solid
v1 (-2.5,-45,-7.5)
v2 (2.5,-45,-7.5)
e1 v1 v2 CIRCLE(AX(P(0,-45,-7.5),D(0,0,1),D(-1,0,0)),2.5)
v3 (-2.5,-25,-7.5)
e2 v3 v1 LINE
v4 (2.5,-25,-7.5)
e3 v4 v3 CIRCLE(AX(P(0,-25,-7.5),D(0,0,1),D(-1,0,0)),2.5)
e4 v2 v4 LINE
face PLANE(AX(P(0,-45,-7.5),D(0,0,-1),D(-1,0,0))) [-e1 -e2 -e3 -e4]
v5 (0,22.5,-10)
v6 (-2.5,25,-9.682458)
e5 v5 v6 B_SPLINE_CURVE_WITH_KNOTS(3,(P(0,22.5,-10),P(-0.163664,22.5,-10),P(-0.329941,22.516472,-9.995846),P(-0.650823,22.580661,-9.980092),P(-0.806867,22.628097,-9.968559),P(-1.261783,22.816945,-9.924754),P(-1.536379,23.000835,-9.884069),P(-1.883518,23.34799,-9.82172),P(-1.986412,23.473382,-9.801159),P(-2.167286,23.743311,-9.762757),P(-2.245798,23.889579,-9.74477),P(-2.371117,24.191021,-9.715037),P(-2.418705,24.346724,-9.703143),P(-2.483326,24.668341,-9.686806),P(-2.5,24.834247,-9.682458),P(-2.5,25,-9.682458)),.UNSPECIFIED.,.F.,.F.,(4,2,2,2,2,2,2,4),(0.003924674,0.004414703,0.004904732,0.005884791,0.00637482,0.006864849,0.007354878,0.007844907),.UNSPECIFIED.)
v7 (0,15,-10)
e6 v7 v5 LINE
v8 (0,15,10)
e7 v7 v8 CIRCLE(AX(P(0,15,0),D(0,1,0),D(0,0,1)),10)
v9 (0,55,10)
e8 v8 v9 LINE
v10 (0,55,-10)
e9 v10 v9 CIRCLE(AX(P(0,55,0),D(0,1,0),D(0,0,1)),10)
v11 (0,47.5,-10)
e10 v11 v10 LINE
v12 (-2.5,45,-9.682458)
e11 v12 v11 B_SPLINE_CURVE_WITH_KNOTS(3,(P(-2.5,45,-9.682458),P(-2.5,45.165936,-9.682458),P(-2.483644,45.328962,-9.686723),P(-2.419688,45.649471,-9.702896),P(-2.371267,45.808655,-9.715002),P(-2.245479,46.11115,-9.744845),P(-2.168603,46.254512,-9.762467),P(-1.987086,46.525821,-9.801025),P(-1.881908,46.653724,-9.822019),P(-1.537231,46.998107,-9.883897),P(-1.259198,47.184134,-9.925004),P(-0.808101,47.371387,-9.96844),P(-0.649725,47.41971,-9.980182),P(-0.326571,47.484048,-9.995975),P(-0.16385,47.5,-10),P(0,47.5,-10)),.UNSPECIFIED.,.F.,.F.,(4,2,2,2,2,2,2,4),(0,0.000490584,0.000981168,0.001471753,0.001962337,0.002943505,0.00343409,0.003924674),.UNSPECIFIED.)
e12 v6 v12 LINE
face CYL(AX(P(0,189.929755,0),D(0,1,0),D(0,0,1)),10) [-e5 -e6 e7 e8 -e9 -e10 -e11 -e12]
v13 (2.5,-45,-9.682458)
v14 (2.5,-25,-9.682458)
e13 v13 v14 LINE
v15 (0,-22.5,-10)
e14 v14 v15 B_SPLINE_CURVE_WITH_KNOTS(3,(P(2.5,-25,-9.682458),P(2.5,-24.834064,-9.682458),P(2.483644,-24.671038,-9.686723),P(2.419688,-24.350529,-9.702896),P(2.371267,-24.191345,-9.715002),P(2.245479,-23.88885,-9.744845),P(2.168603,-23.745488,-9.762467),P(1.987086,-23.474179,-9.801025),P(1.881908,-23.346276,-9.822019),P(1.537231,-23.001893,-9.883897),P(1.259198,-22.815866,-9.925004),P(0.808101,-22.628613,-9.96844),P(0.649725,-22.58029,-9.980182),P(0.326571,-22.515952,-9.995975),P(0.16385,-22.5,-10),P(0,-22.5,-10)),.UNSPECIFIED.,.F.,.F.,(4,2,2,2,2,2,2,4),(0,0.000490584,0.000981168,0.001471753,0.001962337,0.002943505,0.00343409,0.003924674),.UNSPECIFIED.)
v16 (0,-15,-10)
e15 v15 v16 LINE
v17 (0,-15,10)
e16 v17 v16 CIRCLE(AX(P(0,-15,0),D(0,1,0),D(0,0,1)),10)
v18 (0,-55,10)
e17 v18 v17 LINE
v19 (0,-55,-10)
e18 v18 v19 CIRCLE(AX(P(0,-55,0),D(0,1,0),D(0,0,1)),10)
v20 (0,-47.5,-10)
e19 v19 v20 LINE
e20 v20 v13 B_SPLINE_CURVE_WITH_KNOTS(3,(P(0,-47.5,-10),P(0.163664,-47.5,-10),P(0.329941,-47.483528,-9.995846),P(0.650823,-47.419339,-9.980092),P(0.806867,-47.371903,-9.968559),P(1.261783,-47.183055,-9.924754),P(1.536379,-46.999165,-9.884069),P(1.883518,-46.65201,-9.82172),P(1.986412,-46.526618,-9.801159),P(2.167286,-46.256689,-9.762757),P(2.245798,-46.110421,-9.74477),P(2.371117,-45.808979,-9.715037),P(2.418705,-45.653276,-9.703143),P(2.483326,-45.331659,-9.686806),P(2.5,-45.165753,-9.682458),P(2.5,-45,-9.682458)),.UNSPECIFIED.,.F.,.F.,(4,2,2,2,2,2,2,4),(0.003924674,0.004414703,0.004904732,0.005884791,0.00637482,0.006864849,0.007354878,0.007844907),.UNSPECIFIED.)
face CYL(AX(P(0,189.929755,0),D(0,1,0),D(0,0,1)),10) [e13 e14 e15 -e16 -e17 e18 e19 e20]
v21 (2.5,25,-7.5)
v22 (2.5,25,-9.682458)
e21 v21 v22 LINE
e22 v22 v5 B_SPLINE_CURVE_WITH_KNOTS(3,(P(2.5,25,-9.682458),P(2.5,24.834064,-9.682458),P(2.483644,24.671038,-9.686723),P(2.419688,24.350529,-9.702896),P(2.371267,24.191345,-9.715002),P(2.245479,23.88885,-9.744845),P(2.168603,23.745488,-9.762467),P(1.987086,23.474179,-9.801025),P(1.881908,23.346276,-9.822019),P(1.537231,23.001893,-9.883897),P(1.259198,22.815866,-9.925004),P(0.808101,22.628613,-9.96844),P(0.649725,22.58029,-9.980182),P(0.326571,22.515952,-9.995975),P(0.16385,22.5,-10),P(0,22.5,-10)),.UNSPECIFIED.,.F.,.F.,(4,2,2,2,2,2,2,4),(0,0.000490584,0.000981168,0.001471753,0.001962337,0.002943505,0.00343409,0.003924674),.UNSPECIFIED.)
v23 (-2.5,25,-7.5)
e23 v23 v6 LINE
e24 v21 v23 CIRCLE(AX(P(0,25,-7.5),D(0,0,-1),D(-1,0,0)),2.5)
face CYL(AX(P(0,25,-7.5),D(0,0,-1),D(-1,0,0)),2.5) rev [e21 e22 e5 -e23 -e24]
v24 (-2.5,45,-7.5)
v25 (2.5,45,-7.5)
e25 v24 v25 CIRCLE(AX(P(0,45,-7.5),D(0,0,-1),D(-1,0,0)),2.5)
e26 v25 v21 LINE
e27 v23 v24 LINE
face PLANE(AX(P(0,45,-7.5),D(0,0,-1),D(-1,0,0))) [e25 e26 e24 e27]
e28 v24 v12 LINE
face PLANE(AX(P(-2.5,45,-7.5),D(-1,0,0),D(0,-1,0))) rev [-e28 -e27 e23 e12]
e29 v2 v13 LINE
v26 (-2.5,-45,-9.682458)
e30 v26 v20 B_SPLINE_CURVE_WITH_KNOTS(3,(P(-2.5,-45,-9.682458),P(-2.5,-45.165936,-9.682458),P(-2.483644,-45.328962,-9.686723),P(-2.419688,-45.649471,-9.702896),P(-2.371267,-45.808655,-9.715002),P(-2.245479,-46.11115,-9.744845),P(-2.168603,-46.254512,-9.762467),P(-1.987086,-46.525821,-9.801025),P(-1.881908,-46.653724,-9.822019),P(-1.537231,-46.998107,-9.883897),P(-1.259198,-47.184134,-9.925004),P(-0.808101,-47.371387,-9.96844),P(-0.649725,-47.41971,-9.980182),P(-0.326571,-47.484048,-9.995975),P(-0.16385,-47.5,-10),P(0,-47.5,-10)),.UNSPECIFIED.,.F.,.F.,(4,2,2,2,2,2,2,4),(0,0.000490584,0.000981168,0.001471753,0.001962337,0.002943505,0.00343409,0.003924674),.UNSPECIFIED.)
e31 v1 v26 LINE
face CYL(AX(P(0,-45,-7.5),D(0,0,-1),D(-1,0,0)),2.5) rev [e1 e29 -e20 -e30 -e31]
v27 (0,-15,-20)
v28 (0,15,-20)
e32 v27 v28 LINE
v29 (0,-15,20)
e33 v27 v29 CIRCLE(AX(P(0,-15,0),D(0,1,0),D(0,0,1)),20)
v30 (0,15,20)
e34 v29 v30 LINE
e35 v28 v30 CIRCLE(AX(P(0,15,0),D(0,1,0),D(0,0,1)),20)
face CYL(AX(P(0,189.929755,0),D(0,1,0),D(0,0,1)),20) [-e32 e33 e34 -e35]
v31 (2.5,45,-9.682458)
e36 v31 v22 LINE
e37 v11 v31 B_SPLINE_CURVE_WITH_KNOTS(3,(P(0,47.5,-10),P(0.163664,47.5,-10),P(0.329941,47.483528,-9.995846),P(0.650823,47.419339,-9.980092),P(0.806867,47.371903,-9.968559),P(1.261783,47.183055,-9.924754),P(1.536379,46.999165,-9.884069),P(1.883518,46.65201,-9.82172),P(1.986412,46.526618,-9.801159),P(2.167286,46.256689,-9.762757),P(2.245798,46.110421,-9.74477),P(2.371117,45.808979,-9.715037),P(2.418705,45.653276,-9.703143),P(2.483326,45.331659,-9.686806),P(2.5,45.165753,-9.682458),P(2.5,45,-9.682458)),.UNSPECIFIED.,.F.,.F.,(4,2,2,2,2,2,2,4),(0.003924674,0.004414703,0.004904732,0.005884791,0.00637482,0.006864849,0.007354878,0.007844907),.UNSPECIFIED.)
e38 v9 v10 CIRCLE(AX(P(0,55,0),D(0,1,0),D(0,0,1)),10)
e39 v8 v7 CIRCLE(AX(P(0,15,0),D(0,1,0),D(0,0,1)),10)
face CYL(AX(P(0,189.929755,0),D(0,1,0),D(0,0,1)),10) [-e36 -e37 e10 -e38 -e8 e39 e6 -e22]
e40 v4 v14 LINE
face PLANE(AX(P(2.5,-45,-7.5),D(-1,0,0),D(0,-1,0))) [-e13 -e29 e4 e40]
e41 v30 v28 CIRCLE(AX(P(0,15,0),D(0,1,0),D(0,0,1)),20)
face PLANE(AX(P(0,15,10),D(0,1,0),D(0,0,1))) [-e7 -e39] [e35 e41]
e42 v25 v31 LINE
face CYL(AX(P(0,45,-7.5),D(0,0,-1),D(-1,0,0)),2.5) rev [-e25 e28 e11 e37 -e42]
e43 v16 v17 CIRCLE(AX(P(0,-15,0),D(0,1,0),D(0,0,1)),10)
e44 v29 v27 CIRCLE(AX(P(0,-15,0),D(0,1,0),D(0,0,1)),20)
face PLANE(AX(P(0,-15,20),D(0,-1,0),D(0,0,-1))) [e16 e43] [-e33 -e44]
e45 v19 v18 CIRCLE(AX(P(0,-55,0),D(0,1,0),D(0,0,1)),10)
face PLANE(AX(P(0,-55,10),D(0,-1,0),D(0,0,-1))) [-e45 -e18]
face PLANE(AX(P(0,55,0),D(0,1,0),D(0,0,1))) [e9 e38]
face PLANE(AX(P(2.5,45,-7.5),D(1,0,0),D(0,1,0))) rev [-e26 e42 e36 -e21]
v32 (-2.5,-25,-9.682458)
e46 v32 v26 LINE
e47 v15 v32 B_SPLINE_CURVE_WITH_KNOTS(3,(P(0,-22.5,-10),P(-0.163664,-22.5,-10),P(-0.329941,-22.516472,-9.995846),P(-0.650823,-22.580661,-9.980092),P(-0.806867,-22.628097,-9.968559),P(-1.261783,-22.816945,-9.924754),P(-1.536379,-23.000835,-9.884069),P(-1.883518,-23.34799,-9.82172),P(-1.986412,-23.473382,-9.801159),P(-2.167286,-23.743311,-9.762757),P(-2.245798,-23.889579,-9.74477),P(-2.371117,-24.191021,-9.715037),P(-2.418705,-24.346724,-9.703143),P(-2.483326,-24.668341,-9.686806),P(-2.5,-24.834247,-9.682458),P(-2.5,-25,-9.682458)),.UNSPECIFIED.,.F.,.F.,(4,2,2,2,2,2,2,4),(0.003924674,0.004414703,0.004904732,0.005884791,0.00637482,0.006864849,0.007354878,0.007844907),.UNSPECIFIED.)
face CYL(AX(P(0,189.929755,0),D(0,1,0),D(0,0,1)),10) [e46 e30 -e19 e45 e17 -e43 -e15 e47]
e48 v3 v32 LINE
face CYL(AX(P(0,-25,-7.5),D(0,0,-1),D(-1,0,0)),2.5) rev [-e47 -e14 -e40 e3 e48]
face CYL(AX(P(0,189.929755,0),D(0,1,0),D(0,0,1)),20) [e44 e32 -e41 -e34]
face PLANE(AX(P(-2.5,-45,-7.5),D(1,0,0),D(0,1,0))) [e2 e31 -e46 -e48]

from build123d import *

# Parameters (mm, degrees)
CUT_EXTRUDE1_DEPTH = 2.5


with BuildPart() as part:
    # Sketch1 → Revolve1 (revolve)
    with BuildSketch(Plane(origin=(0, 0, 0), x_dir=(0, 0, -1), z_dir=(1, 0, 0))):
        Polygon((0, 55), (-10, 55), (-10, 15), (-20, 15), (-20, -15), (-10, -15), (-10, -55), (0, -55), align=None)
    revolve(axis=Axis((0, 189.929754582, 0), (0, -1, 0)))

    # Sketch2 → Cut-Extrude1 (cut)
    with BuildSketch(Plane(origin=(0, 0, -10), x_dir=(-1, 0, 0), z_dir=(0, 0, -1))):
        with BuildLine():
            Line((2.5, 45), (2.5, 25))
            ThreePointArc((2.5, 25), (0, 22.5), (-2.5, 25))
            Line((-2.5, 25), (-2.5, 45))
            ThreePointArc((-2.5, 45), (0, 47.5), (2.5, 45))
        make_face()
    cut_extrude1 = extrude(amount=-CUT_EXTRUDE1_DEPTH, mode=Mode.SUBTRACT)

    # Mirror1: Cut-Extrude1 across plane
    add(cut_extrude1.mirror(Plane.ZX), mode=Mode.SUBTRACT)


solid = part.part
